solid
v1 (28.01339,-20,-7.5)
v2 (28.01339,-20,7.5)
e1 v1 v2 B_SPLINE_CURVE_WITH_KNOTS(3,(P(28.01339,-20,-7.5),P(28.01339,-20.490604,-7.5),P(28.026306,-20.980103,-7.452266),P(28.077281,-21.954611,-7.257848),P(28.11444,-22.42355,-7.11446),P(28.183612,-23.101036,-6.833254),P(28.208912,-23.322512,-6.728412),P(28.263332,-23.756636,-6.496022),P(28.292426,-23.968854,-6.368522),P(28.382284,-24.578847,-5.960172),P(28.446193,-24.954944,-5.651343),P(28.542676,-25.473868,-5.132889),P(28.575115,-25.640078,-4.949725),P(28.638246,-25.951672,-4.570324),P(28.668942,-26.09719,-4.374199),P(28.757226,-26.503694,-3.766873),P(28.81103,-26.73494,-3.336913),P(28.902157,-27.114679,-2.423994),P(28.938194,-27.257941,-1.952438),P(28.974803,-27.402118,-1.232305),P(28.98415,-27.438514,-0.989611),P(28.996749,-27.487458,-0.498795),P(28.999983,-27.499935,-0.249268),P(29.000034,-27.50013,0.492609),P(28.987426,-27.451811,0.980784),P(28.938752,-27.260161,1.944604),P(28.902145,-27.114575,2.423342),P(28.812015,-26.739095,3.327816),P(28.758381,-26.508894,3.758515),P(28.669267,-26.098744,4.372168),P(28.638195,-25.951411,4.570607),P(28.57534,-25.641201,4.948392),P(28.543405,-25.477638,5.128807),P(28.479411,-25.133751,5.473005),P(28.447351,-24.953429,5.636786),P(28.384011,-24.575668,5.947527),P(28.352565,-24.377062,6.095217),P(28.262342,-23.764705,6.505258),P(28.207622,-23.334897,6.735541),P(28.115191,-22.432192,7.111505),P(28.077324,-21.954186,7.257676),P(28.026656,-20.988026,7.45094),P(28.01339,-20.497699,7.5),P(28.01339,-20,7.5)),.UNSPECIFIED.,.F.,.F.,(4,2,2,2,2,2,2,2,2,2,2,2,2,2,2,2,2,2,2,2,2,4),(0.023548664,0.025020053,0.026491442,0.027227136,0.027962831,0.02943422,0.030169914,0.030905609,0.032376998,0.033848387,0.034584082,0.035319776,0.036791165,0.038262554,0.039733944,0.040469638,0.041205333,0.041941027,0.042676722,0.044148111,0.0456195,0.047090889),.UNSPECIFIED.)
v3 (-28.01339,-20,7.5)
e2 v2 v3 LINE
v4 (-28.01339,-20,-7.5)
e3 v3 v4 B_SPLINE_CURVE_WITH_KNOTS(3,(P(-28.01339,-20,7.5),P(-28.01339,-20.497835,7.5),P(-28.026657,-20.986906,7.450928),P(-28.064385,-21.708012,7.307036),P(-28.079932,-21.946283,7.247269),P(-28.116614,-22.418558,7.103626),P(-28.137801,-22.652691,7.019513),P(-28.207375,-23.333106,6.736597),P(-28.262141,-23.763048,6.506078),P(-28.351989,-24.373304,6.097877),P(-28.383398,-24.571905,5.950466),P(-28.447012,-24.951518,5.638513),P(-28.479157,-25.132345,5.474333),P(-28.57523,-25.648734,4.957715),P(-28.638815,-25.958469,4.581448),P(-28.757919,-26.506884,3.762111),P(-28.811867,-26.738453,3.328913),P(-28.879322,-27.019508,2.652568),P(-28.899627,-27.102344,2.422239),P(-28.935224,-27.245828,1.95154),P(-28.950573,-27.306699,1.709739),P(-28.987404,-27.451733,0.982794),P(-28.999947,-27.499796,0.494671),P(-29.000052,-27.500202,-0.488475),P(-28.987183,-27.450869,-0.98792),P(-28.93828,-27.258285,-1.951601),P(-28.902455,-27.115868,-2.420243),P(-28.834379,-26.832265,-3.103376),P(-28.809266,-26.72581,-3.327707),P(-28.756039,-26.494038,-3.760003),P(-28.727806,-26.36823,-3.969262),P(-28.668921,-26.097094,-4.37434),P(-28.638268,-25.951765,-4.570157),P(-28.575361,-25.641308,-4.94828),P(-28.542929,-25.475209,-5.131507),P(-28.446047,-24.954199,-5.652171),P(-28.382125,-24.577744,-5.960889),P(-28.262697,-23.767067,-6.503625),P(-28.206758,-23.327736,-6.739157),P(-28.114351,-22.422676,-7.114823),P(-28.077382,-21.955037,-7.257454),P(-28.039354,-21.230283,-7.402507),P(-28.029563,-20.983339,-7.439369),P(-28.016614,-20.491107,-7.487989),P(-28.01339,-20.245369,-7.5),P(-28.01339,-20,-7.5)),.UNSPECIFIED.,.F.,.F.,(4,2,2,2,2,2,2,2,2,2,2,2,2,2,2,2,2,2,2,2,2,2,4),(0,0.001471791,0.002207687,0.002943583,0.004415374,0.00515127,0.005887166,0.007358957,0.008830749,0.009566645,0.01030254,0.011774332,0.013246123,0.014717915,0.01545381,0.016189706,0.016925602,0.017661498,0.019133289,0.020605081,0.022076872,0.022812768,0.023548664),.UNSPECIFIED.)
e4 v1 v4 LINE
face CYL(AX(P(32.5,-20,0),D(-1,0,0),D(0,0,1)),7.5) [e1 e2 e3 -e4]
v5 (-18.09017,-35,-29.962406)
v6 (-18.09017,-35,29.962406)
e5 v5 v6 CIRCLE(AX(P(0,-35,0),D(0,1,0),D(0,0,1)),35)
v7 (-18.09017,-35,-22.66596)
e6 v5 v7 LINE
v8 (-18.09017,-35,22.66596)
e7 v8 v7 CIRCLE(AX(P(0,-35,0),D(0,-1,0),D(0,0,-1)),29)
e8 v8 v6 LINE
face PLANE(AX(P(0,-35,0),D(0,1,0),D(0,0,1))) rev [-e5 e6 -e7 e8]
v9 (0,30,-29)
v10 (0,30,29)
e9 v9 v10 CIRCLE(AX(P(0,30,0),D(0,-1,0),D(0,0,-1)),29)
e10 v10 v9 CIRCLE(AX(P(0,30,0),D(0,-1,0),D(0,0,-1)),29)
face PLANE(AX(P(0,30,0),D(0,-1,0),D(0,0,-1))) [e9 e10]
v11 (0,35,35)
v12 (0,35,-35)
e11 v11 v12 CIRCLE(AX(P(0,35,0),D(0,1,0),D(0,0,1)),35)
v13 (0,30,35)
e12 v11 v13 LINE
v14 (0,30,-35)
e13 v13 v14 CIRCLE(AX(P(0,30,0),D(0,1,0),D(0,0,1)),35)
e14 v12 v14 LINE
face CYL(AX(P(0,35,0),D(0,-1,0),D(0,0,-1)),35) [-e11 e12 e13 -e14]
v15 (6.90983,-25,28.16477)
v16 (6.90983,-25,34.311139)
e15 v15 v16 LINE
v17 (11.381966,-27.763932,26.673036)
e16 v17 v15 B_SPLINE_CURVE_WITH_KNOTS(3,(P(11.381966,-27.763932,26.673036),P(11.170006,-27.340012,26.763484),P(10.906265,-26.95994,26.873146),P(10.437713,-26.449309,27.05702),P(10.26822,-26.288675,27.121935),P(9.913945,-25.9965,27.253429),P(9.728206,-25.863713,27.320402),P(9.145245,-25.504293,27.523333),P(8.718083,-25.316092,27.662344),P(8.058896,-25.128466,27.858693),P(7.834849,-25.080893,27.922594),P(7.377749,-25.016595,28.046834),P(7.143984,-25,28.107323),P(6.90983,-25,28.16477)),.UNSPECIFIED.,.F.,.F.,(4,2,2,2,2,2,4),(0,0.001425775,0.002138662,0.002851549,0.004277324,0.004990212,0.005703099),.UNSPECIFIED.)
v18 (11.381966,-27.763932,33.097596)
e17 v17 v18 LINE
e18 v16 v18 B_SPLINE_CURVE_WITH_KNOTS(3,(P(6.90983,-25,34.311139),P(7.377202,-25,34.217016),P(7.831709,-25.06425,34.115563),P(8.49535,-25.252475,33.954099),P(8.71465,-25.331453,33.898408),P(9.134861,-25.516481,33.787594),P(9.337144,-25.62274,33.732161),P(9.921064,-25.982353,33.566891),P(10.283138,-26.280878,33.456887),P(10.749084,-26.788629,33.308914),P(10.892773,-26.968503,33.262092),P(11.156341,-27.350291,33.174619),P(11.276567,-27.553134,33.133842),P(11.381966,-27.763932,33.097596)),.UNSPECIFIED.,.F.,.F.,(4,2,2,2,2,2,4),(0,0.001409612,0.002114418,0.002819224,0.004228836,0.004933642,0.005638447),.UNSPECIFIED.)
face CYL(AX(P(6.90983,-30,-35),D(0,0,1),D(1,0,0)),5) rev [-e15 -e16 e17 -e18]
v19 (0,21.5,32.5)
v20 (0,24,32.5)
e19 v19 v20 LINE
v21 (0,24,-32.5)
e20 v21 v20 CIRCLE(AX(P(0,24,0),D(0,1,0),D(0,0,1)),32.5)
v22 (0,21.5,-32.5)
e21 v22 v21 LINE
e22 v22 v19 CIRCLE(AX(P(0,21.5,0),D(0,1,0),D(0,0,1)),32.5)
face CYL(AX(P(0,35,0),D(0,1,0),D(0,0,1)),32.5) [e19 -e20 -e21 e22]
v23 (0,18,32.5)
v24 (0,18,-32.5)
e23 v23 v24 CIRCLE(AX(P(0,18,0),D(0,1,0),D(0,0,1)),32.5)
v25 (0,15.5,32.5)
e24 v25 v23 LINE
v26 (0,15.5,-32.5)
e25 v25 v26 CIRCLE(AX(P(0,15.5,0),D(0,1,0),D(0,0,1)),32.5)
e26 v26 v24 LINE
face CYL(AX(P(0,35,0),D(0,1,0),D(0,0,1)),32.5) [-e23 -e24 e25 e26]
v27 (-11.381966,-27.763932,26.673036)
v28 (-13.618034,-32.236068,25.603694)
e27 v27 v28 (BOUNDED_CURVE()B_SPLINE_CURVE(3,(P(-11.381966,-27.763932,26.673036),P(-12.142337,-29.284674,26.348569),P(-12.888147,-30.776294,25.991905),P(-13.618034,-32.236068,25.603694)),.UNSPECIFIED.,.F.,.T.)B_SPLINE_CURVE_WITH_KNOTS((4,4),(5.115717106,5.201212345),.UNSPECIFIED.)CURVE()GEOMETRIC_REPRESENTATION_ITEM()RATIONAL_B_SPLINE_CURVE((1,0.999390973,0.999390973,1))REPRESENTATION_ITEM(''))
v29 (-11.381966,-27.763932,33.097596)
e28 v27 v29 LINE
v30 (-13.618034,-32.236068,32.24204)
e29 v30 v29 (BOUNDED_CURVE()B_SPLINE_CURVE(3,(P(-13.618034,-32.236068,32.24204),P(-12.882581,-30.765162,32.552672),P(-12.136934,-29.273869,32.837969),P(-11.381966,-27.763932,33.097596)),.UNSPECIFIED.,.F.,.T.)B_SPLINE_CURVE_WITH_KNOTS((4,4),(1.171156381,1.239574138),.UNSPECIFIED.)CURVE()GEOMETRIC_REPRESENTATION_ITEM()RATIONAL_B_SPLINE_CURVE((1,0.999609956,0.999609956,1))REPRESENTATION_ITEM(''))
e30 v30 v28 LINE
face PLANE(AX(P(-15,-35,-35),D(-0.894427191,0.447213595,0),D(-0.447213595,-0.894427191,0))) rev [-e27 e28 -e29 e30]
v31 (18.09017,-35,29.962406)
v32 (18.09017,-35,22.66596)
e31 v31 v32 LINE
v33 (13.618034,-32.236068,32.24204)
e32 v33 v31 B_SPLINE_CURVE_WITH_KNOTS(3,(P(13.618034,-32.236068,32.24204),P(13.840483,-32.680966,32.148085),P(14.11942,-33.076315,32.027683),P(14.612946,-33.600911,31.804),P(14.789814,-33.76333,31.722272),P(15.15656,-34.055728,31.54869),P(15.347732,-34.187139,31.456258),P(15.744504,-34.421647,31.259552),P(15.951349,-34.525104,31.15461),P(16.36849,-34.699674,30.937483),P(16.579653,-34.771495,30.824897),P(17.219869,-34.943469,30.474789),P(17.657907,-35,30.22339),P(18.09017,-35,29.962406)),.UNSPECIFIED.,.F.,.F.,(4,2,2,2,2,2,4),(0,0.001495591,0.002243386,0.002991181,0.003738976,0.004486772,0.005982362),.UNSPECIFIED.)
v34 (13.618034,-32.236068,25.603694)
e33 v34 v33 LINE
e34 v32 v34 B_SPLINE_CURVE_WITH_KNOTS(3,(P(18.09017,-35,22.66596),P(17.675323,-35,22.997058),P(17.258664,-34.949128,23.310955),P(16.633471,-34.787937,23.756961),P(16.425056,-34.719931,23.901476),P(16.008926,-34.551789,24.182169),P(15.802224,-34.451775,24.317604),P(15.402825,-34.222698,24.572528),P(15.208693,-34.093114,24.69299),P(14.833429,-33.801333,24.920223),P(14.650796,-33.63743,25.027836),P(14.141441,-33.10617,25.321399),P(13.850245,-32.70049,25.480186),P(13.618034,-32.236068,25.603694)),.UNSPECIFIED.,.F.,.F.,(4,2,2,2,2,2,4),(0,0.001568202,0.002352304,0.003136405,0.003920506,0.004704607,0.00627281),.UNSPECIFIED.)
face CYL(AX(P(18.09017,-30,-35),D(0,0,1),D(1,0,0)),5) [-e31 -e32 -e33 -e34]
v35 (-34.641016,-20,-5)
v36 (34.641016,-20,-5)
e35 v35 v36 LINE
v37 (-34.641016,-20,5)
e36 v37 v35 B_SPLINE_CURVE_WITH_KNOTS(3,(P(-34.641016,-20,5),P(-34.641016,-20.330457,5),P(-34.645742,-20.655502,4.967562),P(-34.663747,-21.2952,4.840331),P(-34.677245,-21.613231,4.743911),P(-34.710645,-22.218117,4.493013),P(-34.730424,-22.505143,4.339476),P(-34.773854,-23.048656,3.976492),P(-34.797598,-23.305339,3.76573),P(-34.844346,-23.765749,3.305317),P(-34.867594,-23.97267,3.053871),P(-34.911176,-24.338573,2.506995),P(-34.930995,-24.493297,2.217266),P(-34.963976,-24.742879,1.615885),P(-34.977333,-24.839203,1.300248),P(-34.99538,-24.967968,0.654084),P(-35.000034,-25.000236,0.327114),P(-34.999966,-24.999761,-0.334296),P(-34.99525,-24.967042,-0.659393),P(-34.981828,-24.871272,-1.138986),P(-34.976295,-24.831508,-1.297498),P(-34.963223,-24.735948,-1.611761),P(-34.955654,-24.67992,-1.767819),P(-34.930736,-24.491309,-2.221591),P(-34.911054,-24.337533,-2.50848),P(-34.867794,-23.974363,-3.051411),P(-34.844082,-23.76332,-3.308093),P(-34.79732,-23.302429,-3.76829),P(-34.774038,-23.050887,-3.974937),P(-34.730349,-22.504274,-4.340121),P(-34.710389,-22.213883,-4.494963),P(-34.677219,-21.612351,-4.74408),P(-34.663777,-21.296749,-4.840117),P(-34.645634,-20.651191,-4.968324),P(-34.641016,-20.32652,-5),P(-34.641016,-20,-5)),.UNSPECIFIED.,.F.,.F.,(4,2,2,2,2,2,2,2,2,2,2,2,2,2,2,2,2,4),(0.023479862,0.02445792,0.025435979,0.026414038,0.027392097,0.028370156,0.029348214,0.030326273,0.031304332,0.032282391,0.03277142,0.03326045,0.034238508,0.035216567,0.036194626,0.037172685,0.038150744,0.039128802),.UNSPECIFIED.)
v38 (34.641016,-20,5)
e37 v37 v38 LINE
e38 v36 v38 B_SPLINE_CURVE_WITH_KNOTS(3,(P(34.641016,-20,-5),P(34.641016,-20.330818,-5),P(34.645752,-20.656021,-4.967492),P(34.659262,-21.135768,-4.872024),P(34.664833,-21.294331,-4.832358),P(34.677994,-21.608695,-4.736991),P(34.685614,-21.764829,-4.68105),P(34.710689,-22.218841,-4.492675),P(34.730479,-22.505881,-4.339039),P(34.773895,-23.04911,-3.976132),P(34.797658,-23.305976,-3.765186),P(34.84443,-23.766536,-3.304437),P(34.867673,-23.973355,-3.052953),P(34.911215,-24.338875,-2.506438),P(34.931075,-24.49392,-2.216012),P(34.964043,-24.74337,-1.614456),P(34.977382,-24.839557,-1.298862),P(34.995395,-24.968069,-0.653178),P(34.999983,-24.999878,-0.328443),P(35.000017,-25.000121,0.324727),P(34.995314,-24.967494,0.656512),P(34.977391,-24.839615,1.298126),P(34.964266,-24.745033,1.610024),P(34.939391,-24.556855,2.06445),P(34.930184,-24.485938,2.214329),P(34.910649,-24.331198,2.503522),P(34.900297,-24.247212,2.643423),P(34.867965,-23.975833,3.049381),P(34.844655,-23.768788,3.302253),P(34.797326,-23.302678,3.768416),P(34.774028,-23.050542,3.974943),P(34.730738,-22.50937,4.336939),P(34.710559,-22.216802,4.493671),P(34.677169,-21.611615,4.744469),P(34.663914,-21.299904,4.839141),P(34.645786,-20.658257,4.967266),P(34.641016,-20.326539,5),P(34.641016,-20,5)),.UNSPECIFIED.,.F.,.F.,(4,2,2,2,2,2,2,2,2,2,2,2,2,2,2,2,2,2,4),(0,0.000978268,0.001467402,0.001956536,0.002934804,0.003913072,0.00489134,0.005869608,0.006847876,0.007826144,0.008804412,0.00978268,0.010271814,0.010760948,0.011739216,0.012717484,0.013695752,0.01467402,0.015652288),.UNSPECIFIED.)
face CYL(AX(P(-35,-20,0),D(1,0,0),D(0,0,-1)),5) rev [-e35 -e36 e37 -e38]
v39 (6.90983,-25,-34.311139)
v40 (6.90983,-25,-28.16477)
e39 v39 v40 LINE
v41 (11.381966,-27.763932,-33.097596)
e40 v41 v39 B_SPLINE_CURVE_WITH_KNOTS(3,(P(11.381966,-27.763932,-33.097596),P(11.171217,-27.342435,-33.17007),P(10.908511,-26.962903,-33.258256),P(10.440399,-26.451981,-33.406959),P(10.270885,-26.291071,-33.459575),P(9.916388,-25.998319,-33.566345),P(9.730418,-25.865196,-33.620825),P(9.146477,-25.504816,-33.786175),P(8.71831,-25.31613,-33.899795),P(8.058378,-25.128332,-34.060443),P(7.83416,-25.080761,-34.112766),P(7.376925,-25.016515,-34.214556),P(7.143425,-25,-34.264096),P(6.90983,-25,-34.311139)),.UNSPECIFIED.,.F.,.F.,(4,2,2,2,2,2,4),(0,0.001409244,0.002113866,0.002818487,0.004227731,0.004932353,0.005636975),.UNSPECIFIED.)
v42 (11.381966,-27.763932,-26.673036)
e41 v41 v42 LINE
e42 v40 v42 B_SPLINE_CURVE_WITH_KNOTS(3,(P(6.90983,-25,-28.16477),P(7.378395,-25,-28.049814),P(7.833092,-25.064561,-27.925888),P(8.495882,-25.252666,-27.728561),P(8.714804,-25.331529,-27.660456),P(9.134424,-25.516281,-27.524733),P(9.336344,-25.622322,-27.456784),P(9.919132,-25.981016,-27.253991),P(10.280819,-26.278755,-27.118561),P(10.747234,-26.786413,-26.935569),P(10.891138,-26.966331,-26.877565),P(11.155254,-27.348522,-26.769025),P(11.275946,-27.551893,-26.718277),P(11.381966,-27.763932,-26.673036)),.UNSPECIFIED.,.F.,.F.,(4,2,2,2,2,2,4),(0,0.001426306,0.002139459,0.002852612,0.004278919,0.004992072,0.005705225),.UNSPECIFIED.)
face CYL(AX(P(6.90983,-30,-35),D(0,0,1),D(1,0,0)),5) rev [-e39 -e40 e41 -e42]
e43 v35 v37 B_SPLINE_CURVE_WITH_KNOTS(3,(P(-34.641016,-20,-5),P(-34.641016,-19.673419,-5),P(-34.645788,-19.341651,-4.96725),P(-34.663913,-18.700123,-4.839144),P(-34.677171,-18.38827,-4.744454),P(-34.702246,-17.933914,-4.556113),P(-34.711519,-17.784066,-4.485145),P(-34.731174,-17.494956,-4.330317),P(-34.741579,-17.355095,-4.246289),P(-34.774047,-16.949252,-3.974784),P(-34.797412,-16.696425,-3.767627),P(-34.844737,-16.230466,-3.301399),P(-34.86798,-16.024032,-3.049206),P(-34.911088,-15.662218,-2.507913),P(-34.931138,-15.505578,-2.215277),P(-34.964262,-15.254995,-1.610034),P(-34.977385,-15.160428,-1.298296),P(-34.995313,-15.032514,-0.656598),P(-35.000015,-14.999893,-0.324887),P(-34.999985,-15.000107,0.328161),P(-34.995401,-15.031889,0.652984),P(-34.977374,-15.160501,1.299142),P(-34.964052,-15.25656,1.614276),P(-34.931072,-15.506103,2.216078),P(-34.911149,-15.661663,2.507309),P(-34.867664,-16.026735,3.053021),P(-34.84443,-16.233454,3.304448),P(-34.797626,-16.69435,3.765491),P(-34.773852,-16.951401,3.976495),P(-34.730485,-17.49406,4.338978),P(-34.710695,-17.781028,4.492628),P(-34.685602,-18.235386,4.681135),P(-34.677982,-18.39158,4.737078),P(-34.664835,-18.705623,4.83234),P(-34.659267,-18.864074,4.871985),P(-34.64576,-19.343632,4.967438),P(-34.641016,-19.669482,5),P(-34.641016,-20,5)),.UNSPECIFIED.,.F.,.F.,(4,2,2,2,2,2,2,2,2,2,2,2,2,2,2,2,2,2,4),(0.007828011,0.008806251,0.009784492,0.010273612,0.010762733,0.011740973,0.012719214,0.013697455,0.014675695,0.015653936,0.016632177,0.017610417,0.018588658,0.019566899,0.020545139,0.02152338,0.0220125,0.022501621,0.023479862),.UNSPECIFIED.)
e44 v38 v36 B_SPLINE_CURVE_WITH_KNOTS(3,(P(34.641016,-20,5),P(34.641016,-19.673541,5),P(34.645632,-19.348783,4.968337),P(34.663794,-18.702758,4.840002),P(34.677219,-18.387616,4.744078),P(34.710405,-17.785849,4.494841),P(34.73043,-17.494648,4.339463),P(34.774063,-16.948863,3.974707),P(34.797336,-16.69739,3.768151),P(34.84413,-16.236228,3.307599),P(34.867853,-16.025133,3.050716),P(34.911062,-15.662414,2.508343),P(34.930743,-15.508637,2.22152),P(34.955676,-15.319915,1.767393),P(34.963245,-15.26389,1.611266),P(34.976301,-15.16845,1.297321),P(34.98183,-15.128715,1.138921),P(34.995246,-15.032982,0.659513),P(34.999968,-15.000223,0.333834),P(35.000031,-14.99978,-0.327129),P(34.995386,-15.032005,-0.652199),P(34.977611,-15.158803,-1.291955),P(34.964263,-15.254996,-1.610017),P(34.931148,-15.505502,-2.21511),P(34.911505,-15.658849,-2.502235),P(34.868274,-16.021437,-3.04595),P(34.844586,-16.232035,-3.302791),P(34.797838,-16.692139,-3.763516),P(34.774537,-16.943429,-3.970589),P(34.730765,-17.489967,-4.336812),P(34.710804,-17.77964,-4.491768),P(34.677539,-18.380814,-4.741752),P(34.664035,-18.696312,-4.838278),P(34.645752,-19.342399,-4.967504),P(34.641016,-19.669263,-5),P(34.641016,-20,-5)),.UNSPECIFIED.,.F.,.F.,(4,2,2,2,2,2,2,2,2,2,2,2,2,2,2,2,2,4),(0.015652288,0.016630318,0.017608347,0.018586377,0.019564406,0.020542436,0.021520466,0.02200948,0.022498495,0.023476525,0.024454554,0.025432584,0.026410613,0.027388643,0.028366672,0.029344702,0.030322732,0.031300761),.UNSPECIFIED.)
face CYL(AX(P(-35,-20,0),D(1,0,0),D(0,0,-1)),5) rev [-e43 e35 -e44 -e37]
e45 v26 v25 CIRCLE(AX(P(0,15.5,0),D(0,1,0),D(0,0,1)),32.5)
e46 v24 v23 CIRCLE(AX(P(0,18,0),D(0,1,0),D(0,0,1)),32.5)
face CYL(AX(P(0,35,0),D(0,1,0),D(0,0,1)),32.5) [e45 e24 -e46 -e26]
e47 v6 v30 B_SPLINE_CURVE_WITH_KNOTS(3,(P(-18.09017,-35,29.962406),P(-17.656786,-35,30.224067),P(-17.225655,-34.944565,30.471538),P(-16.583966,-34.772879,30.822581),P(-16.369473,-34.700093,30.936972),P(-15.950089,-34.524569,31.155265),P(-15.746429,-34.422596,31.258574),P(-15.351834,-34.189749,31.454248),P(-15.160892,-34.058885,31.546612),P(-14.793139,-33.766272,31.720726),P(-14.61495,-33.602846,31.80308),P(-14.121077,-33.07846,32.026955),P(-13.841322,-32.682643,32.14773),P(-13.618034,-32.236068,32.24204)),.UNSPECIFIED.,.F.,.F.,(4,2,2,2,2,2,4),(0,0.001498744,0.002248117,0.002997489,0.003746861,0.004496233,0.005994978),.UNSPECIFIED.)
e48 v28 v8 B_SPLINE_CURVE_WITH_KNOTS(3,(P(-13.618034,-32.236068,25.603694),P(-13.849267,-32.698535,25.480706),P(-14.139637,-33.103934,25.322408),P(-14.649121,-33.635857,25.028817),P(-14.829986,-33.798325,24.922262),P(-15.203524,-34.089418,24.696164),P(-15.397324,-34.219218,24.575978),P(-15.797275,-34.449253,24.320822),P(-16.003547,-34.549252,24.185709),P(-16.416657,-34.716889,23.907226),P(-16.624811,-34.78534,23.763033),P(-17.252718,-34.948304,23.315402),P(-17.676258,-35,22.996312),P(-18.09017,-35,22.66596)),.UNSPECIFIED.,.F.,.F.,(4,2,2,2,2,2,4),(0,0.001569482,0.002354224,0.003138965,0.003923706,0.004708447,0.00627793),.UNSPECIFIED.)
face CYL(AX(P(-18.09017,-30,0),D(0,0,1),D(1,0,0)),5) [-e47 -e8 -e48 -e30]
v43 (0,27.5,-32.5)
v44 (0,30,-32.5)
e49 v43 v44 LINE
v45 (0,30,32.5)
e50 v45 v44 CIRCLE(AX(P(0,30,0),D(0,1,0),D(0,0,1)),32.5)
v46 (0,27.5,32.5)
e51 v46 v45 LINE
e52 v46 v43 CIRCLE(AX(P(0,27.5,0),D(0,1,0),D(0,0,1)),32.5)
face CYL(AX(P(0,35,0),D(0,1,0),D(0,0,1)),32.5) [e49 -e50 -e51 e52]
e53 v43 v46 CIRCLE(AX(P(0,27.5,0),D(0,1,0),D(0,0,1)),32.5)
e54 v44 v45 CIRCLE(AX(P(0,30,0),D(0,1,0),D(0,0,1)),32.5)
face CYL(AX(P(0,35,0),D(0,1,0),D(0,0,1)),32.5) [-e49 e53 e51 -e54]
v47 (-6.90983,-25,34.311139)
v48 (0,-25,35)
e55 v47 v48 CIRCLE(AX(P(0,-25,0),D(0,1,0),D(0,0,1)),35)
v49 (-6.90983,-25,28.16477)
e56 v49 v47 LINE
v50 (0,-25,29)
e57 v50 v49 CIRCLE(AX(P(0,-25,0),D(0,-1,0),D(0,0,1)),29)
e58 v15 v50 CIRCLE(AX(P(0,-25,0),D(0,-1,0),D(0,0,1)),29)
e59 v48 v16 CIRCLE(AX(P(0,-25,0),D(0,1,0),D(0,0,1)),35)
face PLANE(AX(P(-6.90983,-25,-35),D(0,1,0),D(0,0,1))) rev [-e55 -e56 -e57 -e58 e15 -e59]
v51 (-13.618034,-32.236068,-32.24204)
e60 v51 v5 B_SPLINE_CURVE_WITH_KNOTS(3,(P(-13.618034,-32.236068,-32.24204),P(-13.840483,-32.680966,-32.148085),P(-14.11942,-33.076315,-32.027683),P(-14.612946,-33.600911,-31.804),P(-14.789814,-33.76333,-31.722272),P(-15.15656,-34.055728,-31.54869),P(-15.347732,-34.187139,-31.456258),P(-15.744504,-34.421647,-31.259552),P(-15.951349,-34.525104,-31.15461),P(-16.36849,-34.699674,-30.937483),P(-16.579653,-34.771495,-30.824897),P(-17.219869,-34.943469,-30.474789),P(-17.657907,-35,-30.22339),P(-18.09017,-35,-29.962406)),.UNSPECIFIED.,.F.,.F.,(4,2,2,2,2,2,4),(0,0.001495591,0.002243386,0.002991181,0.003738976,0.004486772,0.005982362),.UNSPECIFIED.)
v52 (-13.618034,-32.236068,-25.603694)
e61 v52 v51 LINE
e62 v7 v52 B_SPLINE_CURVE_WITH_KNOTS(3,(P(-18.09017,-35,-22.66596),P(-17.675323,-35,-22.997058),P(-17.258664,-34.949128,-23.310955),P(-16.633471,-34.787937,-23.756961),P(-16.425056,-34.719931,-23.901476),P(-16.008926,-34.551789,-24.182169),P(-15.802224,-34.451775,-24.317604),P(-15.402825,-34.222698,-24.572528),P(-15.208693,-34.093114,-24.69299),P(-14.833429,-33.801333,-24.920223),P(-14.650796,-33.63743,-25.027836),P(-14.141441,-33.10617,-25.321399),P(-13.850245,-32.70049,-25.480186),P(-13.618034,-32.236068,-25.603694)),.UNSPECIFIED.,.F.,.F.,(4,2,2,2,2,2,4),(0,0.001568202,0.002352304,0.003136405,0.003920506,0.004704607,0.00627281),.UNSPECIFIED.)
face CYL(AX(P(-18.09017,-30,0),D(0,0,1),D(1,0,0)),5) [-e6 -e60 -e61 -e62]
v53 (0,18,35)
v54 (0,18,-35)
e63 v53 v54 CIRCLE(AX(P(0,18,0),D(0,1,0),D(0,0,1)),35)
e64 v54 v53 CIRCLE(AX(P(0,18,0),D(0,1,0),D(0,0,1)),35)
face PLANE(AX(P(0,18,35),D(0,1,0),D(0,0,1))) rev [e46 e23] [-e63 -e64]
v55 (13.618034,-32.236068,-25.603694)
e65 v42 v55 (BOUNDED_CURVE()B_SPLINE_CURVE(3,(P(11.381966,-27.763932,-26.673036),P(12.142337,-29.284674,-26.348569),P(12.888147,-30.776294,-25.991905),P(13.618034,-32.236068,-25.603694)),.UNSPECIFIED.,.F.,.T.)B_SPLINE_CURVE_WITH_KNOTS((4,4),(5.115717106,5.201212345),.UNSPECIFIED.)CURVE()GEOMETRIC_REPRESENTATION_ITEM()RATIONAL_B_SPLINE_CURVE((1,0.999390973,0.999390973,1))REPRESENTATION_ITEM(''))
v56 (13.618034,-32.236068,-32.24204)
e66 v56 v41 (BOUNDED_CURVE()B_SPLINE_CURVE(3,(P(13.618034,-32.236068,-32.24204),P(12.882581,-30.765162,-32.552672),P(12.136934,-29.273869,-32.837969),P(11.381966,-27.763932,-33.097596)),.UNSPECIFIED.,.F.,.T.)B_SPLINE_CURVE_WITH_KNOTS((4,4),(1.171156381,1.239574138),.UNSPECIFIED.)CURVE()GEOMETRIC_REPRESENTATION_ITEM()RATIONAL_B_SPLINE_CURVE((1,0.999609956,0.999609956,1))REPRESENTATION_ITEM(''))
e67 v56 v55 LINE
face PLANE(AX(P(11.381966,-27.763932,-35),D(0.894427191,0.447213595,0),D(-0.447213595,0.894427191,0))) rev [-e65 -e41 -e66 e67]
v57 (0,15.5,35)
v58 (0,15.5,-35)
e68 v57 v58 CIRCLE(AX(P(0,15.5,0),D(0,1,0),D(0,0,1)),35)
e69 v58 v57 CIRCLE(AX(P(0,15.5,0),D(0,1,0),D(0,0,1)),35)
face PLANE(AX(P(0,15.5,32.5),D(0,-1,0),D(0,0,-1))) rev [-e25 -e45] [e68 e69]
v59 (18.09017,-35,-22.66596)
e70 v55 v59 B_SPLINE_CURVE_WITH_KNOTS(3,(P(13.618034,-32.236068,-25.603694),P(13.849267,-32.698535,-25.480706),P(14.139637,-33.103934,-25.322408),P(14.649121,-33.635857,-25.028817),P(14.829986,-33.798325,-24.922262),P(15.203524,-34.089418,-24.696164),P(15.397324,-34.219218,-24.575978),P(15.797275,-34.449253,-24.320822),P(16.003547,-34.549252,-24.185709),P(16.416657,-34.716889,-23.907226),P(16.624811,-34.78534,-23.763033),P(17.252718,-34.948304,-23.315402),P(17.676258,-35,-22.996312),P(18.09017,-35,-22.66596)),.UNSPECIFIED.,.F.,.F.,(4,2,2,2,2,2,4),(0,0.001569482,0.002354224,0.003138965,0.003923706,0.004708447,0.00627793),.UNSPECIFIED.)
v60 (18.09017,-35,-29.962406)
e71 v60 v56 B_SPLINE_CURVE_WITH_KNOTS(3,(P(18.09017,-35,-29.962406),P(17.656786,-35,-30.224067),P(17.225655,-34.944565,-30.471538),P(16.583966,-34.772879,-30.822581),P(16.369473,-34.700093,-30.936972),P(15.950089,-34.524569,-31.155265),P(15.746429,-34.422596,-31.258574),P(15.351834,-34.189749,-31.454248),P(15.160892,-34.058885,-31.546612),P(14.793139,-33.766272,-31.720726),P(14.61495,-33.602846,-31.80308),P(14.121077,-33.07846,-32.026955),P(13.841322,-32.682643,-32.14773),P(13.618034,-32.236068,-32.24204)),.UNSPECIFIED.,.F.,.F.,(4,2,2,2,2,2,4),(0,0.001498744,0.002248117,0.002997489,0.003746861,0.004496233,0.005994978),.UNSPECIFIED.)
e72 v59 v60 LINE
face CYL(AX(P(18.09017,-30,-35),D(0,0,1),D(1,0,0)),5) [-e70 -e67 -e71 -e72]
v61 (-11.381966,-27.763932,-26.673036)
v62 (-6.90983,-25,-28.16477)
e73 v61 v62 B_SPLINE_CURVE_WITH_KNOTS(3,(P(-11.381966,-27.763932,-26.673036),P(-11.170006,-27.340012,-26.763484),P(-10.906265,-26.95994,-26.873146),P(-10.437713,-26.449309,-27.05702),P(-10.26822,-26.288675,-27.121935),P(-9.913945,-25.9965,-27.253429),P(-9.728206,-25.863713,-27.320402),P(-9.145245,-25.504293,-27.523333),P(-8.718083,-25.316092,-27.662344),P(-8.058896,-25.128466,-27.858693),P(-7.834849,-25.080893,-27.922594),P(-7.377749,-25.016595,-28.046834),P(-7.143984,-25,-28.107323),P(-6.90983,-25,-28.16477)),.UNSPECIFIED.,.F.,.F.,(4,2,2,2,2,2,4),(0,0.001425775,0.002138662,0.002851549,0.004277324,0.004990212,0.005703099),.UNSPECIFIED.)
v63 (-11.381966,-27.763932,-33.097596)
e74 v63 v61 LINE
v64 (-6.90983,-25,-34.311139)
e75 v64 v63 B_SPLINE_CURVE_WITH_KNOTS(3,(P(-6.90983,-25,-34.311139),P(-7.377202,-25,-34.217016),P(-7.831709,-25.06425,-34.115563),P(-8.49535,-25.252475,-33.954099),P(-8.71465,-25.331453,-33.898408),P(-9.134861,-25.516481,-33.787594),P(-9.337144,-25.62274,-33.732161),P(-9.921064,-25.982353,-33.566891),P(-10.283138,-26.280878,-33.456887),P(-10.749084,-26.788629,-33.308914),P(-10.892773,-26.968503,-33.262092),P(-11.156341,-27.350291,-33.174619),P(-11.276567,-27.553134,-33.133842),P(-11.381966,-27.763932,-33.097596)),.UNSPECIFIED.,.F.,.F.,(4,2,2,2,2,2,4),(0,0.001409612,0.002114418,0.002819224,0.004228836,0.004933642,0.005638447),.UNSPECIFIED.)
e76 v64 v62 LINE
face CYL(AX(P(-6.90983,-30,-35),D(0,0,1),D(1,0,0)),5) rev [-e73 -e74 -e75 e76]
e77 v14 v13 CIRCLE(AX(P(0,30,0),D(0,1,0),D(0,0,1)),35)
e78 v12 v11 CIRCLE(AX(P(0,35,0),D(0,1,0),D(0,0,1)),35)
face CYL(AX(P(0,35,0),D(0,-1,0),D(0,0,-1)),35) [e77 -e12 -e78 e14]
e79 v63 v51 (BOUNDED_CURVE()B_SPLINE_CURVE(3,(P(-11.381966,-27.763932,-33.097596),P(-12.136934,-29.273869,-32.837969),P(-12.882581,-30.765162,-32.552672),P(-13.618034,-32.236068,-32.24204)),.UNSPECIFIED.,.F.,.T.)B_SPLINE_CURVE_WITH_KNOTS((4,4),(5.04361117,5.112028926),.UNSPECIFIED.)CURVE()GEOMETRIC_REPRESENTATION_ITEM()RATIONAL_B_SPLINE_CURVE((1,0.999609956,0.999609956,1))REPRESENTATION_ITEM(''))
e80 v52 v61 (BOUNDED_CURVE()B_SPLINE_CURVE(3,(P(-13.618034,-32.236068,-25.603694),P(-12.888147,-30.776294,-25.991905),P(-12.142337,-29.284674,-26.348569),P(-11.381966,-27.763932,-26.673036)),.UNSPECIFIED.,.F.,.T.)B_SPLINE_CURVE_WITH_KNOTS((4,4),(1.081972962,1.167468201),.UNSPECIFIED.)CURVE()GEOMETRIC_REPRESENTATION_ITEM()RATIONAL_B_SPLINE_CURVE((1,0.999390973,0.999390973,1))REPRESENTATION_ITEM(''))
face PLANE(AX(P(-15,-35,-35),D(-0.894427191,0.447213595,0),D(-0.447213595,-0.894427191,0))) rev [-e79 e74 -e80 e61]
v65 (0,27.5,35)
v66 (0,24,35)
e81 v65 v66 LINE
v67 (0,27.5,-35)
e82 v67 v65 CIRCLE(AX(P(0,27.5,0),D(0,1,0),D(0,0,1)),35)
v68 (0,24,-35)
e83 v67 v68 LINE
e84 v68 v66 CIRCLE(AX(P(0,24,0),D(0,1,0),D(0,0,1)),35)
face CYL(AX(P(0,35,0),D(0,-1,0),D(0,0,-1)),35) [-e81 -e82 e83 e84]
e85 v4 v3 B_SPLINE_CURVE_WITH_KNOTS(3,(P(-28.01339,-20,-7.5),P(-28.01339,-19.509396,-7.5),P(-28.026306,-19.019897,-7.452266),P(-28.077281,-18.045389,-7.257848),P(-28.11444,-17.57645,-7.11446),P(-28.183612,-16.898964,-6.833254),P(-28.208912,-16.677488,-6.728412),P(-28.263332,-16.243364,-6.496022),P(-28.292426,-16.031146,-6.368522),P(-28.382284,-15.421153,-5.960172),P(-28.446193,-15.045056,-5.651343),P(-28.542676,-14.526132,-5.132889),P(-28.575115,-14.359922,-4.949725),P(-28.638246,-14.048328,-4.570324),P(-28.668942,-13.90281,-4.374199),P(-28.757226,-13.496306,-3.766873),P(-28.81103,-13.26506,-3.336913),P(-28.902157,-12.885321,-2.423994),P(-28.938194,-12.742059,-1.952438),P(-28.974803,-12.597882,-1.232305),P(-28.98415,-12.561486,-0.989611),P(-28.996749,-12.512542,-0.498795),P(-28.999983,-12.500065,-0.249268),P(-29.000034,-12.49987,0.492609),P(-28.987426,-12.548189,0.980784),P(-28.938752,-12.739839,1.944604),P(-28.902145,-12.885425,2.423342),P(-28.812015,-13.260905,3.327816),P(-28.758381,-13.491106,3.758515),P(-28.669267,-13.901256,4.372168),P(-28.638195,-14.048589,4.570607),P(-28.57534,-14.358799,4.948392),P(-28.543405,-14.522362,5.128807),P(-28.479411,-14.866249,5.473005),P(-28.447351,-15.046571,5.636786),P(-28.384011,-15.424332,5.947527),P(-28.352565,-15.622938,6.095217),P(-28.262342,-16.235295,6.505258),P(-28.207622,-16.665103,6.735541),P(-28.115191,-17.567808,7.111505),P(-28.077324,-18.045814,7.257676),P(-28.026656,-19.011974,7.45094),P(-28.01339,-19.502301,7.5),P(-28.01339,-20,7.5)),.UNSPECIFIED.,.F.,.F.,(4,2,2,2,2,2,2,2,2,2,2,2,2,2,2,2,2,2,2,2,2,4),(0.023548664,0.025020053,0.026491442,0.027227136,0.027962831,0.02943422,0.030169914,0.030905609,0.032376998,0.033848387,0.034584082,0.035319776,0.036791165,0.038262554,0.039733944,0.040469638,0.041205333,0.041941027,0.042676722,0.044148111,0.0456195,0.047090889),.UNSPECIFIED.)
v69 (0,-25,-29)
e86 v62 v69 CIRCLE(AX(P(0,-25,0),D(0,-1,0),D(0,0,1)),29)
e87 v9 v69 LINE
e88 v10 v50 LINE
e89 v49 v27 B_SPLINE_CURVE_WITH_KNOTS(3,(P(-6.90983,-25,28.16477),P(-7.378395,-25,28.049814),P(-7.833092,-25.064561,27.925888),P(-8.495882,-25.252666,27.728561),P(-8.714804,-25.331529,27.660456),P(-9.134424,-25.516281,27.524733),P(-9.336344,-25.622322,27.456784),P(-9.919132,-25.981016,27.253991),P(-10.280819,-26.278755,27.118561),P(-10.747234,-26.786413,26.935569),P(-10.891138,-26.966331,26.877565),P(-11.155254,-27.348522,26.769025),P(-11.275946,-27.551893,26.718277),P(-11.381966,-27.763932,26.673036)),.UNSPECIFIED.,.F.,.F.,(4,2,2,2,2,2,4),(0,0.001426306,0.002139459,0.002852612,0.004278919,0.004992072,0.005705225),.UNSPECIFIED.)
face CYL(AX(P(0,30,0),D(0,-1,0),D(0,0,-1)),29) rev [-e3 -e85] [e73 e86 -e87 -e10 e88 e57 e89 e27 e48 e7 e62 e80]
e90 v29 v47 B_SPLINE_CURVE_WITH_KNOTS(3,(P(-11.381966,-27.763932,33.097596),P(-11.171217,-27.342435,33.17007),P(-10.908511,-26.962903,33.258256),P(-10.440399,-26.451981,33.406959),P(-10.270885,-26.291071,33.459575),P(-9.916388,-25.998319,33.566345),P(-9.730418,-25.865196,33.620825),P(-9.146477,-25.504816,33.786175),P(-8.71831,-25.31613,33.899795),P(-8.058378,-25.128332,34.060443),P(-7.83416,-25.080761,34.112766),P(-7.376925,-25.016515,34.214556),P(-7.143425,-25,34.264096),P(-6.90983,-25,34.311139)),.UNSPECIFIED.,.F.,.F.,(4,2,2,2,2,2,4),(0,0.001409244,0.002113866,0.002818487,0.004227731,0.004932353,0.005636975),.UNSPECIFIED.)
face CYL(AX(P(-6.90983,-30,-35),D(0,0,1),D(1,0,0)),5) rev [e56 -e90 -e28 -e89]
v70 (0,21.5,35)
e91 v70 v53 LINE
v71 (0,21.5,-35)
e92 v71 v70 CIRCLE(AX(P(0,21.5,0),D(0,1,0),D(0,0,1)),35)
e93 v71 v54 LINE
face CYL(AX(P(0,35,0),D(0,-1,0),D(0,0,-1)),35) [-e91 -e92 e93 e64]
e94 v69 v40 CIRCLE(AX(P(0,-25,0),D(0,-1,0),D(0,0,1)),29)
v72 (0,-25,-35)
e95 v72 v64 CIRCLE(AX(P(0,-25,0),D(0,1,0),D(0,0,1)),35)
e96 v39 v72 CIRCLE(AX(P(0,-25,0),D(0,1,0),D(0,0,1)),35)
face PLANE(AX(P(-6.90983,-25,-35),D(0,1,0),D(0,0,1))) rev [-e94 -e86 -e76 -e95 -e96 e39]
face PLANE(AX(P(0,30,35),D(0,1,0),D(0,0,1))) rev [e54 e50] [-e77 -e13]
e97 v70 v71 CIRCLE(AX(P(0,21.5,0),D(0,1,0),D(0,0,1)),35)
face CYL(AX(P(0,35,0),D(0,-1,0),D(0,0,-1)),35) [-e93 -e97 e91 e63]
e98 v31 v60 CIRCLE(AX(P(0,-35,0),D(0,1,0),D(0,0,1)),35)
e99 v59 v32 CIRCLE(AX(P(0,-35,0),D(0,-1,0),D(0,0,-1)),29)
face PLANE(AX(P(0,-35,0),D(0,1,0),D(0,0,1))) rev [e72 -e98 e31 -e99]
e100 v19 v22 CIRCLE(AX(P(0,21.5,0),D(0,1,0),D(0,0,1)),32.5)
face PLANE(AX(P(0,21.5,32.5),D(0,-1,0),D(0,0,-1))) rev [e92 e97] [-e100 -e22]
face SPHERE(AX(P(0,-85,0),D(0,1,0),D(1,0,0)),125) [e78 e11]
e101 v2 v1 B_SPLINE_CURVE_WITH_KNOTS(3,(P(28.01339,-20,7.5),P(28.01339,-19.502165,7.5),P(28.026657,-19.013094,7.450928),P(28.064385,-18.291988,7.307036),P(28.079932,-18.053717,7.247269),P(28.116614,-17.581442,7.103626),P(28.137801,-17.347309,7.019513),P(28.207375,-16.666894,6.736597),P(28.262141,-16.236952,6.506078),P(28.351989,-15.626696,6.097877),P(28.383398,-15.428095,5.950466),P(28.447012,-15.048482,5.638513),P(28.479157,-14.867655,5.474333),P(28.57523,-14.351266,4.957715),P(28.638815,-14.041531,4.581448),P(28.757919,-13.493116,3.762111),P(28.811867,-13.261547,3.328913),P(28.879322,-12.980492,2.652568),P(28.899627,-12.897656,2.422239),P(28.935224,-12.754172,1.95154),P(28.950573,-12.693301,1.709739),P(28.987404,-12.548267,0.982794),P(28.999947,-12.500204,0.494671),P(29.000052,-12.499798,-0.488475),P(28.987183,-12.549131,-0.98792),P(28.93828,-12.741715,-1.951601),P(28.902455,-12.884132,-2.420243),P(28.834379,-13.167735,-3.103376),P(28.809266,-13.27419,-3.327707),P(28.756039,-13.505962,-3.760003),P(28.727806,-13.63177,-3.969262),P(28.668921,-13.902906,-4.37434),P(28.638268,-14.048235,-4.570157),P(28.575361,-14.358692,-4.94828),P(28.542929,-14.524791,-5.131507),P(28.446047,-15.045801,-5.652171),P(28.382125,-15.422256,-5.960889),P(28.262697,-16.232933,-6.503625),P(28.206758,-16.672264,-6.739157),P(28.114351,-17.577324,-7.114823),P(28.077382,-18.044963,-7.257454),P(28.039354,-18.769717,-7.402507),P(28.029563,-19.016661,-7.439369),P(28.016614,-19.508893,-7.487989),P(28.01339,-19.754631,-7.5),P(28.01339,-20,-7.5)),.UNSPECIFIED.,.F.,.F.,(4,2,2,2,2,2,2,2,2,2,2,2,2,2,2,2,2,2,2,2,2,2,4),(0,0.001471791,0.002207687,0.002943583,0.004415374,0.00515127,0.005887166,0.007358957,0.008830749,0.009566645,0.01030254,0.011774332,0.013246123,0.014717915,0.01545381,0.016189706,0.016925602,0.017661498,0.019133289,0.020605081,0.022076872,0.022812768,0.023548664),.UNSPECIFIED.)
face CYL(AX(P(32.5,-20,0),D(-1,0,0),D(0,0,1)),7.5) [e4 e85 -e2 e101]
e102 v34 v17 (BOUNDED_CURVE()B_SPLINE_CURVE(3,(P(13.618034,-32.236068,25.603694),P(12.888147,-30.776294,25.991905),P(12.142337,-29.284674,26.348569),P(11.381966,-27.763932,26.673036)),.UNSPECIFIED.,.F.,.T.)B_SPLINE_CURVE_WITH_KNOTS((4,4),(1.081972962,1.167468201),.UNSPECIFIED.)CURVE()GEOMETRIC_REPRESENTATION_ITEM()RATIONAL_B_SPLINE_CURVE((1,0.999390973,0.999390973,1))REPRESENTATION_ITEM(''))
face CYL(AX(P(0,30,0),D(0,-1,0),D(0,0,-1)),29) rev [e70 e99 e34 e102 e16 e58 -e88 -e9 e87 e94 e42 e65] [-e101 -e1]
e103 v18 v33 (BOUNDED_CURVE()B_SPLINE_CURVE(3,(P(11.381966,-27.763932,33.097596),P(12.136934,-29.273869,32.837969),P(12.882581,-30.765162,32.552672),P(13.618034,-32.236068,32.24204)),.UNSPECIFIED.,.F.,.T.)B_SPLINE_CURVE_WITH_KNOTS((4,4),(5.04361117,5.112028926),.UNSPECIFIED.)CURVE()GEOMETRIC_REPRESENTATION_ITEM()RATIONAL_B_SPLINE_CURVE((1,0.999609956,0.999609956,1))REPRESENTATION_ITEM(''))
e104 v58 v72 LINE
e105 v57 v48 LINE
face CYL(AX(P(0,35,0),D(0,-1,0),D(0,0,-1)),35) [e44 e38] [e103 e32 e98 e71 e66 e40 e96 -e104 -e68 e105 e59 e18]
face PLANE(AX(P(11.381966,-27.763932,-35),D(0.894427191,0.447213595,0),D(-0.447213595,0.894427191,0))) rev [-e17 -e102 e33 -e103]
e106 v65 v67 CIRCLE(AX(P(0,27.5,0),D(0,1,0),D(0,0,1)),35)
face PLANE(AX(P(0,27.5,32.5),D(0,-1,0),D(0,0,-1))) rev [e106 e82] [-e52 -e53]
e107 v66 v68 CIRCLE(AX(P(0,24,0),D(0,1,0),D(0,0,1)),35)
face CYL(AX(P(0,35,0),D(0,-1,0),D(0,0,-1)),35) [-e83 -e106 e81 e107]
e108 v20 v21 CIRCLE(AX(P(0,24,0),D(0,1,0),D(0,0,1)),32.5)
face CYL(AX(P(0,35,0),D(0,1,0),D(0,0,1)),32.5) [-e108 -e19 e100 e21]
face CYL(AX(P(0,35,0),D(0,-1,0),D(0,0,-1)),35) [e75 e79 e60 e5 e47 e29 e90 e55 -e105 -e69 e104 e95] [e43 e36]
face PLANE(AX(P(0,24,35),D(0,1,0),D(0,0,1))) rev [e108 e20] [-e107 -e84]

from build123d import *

# Parameters (mm, degrees)
PISTON_BODY_SKETCH_R       = 35
PISTON_BODY_70_DEPTH       = 35
RING_GROOVES_SKETCH_W      = 2.5
RING_GROOVES_SKETCH_H      = 2.5
INNER_BORE_SKETCH_R        = 29
INNER_BORE_58_DEPTH        = 65
SKIRT_CUTOUTS_DEPTH        = 61.621778265
SKIRT_CUTOUTS_DEPTH_BACK   = 61.621778265
SKIRT_CUTOUT_FILLET_R5_R   = 5
PIN_HOLE_10_DEPTH          = 61.621778438
PIN_HOLE_10_DEPTH_BACK     = 61.621778438
PIN_HOLE_SKETCH_R          = 5
PIN_BOSS_SKETCH_R          = 7.5
PIN_BOSS_15_DEPTH          = 32.5
PIN_BORE_DEPTH             = 84.703345378
PIN_BORE_DEPTH_BACK        = 84.703345378
PIN_BORE_SKETCH_R          = 5
CROWN_DOME_5MM_FACE_RADIUS = 35
CROWN_DOME_5MM_HEIGHT      = 5


with BuildPart() as part:
    # Piston Body Sketch → Piston Body _70 (new, symmetric)
    with BuildSketch(Plane(origin=(0, 0, 0), x_dir=(1, 0, 0), z_dir=(0, 1, 0))):
        with Locations(Location((0, 0, 0), (0, 0, 270))):
            Circle(PISTON_BODY_SKETCH_R)
    extrude(amount=PISTON_BODY_70_DEPTH, both=True)

    # Ring Grooves Sketch → Ring Grooves (revolve, cut)
    with BuildSketch(Plane(origin=(0, 0, 0), x_dir=(0, 0, -1), z_dir=(1, 0, 0))):
        with Locations((-33.75, 28.75)):
            Rectangle(RING_GROOVES_SKETCH_W, RING_GROOVES_SKETCH_H)
        with Locations((-33.75, 22.75)):
            Rectangle(RING_GROOVES_SKETCH_W, RING_GROOVES_SKETCH_H)
        with Locations((-33.75, 16.75)):
            Rectangle(RING_GROOVES_SKETCH_W, RING_GROOVES_SKETCH_H)
    revolve(axis=Axis((0, 35, 0), (0, -1, 0)), mode=Mode.SUBTRACT)

    # Inner Bore Sketch → Inner Bore _58 (cut)
    with BuildSketch(Plane.XZ.offset(35)):
        with Locations(Location((0, 0, 0), (0, 0, 270))):
            Circle(INNER_BORE_SKETCH_R)
    extrude(amount=-INNER_BORE_58_DEPTH, mode=Mode.SUBTRACT)

    # Skirt Cutout Sketch → Skirt Cutouts (cut, two sides: drawn at the far end of the back side and taken through both)
    with BuildSketch(Plane.XY.offset(-SKIRT_CUTOUTS_DEPTH_BACK)):
        with BuildLine():
            Line((15, -35), (-15, -35))
            Line((-15, -35), (-11.381966011, -27.763932023))
            ThreePointArc((-11.381966011, -27.763932023), (-9.538485617, -25.746745958), (-6.909830056, -25))
            Line((-6.909830056, -25), (6.909830056, -25))
            ThreePointArc((6.909830056, -25), (9.538485617, -25.746745958), (11.381966011, -27.763932023))
            Line((11.381966011, -27.763932023), (15, -35))
        make_face()
    extrude(amount=SKIRT_CUTOUTS_DEPTH + SKIRT_CUTOUTS_DEPTH_BACK, mode=Mode.SUBTRACT)

    # Skirt Cutout Fillet R5
    skirt_cutout_fillet_r5_edges = [part.edges().sort_by_distance(p)[0] for p in [
        (15, -35, -28.221061947),
        (15, -35, 28.221061947),
        (-15, -35, -28.221061947),
        (-15, -35, 28.221061947),
    ]]
    fillet(skirt_cutout_fillet_r5_edges, radius=SKIRT_CUTOUT_FILLET_R5_R)

    # Pin Hole Sketch → Pin Hole _10 (cut, two sides: drawn at the far end of the back side and taken through both)
    with BuildSketch(Plane(origin=(0, 0, 0), x_dir=(0, 0, -1), z_dir=(1, 0, 0)).offset(-PIN_HOLE_10_DEPTH_BACK)):
        with Locations((0, -20)):
            Circle(PIN_HOLE_SKETCH_R)
    extrude(amount=PIN_HOLE_10_DEPTH + PIN_HOLE_10_DEPTH_BACK, mode=Mode.SUBTRACT)

    # Pin Boss Sketch → Pin Boss _15 (add, symmetric)
    with BuildSketch(Plane(origin=(0, 0, 0), x_dir=(0, 0, -1), z_dir=(1, 0, 0))):
        with Locations(Location((0, -20, 0), (0, 0, 180))):
            Circle(PIN_BOSS_SKETCH_R)
    extrude(amount=PIN_BOSS_15_DEPTH, both=True)

    # Pin Bore Sketch → Pin Bore (cut, two sides: drawn at the far end of the back side and taken through both)
    with BuildSketch(Plane(origin=(32.5, 0, 0), x_dir=(0, 0, -1), z_dir=(1, 0, 0)).offset(-PIN_BORE_DEPTH_BACK)):
        with Locations((0, -20)):
            Circle(PIN_BORE_SKETCH_R)
    extrude(amount=PIN_BORE_DEPTH + PIN_BORE_DEPTH_BACK, mode=Mode.SUBTRACT)

    # Crown Dome 5mm: a dome of height H over a round flat face of radius A is a cap of a sphere of radius (A * A + H * H) / (2 * H)
    crown_dome_5mm_r = (CROWN_DOME_5MM_FACE_RADIUS * CROWN_DOME_5MM_FACE_RADIUS + CROWN_DOME_5MM_HEIGHT * CROWN_DOME_5MM_HEIGHT) / (2 * CROWN_DOME_5MM_HEIGHT)
    crown_dome_5mm_base = Plane((0, 35, 0), z_dir=(0, 1, 0))
    with Locations(crown_dome_5mm_base.offset(CROWN_DOME_5MM_HEIGHT - crown_dome_5mm_r)):
        crown_dome_5mm_ball = Sphere(crown_dome_5mm_r, mode=Mode.PRIVATE)
    add(split(crown_dome_5mm_ball, bisect_by=crown_dome_5mm_base, keep=Keep.TOP, mode=Mode.PRIVATE))


solid = part.part
